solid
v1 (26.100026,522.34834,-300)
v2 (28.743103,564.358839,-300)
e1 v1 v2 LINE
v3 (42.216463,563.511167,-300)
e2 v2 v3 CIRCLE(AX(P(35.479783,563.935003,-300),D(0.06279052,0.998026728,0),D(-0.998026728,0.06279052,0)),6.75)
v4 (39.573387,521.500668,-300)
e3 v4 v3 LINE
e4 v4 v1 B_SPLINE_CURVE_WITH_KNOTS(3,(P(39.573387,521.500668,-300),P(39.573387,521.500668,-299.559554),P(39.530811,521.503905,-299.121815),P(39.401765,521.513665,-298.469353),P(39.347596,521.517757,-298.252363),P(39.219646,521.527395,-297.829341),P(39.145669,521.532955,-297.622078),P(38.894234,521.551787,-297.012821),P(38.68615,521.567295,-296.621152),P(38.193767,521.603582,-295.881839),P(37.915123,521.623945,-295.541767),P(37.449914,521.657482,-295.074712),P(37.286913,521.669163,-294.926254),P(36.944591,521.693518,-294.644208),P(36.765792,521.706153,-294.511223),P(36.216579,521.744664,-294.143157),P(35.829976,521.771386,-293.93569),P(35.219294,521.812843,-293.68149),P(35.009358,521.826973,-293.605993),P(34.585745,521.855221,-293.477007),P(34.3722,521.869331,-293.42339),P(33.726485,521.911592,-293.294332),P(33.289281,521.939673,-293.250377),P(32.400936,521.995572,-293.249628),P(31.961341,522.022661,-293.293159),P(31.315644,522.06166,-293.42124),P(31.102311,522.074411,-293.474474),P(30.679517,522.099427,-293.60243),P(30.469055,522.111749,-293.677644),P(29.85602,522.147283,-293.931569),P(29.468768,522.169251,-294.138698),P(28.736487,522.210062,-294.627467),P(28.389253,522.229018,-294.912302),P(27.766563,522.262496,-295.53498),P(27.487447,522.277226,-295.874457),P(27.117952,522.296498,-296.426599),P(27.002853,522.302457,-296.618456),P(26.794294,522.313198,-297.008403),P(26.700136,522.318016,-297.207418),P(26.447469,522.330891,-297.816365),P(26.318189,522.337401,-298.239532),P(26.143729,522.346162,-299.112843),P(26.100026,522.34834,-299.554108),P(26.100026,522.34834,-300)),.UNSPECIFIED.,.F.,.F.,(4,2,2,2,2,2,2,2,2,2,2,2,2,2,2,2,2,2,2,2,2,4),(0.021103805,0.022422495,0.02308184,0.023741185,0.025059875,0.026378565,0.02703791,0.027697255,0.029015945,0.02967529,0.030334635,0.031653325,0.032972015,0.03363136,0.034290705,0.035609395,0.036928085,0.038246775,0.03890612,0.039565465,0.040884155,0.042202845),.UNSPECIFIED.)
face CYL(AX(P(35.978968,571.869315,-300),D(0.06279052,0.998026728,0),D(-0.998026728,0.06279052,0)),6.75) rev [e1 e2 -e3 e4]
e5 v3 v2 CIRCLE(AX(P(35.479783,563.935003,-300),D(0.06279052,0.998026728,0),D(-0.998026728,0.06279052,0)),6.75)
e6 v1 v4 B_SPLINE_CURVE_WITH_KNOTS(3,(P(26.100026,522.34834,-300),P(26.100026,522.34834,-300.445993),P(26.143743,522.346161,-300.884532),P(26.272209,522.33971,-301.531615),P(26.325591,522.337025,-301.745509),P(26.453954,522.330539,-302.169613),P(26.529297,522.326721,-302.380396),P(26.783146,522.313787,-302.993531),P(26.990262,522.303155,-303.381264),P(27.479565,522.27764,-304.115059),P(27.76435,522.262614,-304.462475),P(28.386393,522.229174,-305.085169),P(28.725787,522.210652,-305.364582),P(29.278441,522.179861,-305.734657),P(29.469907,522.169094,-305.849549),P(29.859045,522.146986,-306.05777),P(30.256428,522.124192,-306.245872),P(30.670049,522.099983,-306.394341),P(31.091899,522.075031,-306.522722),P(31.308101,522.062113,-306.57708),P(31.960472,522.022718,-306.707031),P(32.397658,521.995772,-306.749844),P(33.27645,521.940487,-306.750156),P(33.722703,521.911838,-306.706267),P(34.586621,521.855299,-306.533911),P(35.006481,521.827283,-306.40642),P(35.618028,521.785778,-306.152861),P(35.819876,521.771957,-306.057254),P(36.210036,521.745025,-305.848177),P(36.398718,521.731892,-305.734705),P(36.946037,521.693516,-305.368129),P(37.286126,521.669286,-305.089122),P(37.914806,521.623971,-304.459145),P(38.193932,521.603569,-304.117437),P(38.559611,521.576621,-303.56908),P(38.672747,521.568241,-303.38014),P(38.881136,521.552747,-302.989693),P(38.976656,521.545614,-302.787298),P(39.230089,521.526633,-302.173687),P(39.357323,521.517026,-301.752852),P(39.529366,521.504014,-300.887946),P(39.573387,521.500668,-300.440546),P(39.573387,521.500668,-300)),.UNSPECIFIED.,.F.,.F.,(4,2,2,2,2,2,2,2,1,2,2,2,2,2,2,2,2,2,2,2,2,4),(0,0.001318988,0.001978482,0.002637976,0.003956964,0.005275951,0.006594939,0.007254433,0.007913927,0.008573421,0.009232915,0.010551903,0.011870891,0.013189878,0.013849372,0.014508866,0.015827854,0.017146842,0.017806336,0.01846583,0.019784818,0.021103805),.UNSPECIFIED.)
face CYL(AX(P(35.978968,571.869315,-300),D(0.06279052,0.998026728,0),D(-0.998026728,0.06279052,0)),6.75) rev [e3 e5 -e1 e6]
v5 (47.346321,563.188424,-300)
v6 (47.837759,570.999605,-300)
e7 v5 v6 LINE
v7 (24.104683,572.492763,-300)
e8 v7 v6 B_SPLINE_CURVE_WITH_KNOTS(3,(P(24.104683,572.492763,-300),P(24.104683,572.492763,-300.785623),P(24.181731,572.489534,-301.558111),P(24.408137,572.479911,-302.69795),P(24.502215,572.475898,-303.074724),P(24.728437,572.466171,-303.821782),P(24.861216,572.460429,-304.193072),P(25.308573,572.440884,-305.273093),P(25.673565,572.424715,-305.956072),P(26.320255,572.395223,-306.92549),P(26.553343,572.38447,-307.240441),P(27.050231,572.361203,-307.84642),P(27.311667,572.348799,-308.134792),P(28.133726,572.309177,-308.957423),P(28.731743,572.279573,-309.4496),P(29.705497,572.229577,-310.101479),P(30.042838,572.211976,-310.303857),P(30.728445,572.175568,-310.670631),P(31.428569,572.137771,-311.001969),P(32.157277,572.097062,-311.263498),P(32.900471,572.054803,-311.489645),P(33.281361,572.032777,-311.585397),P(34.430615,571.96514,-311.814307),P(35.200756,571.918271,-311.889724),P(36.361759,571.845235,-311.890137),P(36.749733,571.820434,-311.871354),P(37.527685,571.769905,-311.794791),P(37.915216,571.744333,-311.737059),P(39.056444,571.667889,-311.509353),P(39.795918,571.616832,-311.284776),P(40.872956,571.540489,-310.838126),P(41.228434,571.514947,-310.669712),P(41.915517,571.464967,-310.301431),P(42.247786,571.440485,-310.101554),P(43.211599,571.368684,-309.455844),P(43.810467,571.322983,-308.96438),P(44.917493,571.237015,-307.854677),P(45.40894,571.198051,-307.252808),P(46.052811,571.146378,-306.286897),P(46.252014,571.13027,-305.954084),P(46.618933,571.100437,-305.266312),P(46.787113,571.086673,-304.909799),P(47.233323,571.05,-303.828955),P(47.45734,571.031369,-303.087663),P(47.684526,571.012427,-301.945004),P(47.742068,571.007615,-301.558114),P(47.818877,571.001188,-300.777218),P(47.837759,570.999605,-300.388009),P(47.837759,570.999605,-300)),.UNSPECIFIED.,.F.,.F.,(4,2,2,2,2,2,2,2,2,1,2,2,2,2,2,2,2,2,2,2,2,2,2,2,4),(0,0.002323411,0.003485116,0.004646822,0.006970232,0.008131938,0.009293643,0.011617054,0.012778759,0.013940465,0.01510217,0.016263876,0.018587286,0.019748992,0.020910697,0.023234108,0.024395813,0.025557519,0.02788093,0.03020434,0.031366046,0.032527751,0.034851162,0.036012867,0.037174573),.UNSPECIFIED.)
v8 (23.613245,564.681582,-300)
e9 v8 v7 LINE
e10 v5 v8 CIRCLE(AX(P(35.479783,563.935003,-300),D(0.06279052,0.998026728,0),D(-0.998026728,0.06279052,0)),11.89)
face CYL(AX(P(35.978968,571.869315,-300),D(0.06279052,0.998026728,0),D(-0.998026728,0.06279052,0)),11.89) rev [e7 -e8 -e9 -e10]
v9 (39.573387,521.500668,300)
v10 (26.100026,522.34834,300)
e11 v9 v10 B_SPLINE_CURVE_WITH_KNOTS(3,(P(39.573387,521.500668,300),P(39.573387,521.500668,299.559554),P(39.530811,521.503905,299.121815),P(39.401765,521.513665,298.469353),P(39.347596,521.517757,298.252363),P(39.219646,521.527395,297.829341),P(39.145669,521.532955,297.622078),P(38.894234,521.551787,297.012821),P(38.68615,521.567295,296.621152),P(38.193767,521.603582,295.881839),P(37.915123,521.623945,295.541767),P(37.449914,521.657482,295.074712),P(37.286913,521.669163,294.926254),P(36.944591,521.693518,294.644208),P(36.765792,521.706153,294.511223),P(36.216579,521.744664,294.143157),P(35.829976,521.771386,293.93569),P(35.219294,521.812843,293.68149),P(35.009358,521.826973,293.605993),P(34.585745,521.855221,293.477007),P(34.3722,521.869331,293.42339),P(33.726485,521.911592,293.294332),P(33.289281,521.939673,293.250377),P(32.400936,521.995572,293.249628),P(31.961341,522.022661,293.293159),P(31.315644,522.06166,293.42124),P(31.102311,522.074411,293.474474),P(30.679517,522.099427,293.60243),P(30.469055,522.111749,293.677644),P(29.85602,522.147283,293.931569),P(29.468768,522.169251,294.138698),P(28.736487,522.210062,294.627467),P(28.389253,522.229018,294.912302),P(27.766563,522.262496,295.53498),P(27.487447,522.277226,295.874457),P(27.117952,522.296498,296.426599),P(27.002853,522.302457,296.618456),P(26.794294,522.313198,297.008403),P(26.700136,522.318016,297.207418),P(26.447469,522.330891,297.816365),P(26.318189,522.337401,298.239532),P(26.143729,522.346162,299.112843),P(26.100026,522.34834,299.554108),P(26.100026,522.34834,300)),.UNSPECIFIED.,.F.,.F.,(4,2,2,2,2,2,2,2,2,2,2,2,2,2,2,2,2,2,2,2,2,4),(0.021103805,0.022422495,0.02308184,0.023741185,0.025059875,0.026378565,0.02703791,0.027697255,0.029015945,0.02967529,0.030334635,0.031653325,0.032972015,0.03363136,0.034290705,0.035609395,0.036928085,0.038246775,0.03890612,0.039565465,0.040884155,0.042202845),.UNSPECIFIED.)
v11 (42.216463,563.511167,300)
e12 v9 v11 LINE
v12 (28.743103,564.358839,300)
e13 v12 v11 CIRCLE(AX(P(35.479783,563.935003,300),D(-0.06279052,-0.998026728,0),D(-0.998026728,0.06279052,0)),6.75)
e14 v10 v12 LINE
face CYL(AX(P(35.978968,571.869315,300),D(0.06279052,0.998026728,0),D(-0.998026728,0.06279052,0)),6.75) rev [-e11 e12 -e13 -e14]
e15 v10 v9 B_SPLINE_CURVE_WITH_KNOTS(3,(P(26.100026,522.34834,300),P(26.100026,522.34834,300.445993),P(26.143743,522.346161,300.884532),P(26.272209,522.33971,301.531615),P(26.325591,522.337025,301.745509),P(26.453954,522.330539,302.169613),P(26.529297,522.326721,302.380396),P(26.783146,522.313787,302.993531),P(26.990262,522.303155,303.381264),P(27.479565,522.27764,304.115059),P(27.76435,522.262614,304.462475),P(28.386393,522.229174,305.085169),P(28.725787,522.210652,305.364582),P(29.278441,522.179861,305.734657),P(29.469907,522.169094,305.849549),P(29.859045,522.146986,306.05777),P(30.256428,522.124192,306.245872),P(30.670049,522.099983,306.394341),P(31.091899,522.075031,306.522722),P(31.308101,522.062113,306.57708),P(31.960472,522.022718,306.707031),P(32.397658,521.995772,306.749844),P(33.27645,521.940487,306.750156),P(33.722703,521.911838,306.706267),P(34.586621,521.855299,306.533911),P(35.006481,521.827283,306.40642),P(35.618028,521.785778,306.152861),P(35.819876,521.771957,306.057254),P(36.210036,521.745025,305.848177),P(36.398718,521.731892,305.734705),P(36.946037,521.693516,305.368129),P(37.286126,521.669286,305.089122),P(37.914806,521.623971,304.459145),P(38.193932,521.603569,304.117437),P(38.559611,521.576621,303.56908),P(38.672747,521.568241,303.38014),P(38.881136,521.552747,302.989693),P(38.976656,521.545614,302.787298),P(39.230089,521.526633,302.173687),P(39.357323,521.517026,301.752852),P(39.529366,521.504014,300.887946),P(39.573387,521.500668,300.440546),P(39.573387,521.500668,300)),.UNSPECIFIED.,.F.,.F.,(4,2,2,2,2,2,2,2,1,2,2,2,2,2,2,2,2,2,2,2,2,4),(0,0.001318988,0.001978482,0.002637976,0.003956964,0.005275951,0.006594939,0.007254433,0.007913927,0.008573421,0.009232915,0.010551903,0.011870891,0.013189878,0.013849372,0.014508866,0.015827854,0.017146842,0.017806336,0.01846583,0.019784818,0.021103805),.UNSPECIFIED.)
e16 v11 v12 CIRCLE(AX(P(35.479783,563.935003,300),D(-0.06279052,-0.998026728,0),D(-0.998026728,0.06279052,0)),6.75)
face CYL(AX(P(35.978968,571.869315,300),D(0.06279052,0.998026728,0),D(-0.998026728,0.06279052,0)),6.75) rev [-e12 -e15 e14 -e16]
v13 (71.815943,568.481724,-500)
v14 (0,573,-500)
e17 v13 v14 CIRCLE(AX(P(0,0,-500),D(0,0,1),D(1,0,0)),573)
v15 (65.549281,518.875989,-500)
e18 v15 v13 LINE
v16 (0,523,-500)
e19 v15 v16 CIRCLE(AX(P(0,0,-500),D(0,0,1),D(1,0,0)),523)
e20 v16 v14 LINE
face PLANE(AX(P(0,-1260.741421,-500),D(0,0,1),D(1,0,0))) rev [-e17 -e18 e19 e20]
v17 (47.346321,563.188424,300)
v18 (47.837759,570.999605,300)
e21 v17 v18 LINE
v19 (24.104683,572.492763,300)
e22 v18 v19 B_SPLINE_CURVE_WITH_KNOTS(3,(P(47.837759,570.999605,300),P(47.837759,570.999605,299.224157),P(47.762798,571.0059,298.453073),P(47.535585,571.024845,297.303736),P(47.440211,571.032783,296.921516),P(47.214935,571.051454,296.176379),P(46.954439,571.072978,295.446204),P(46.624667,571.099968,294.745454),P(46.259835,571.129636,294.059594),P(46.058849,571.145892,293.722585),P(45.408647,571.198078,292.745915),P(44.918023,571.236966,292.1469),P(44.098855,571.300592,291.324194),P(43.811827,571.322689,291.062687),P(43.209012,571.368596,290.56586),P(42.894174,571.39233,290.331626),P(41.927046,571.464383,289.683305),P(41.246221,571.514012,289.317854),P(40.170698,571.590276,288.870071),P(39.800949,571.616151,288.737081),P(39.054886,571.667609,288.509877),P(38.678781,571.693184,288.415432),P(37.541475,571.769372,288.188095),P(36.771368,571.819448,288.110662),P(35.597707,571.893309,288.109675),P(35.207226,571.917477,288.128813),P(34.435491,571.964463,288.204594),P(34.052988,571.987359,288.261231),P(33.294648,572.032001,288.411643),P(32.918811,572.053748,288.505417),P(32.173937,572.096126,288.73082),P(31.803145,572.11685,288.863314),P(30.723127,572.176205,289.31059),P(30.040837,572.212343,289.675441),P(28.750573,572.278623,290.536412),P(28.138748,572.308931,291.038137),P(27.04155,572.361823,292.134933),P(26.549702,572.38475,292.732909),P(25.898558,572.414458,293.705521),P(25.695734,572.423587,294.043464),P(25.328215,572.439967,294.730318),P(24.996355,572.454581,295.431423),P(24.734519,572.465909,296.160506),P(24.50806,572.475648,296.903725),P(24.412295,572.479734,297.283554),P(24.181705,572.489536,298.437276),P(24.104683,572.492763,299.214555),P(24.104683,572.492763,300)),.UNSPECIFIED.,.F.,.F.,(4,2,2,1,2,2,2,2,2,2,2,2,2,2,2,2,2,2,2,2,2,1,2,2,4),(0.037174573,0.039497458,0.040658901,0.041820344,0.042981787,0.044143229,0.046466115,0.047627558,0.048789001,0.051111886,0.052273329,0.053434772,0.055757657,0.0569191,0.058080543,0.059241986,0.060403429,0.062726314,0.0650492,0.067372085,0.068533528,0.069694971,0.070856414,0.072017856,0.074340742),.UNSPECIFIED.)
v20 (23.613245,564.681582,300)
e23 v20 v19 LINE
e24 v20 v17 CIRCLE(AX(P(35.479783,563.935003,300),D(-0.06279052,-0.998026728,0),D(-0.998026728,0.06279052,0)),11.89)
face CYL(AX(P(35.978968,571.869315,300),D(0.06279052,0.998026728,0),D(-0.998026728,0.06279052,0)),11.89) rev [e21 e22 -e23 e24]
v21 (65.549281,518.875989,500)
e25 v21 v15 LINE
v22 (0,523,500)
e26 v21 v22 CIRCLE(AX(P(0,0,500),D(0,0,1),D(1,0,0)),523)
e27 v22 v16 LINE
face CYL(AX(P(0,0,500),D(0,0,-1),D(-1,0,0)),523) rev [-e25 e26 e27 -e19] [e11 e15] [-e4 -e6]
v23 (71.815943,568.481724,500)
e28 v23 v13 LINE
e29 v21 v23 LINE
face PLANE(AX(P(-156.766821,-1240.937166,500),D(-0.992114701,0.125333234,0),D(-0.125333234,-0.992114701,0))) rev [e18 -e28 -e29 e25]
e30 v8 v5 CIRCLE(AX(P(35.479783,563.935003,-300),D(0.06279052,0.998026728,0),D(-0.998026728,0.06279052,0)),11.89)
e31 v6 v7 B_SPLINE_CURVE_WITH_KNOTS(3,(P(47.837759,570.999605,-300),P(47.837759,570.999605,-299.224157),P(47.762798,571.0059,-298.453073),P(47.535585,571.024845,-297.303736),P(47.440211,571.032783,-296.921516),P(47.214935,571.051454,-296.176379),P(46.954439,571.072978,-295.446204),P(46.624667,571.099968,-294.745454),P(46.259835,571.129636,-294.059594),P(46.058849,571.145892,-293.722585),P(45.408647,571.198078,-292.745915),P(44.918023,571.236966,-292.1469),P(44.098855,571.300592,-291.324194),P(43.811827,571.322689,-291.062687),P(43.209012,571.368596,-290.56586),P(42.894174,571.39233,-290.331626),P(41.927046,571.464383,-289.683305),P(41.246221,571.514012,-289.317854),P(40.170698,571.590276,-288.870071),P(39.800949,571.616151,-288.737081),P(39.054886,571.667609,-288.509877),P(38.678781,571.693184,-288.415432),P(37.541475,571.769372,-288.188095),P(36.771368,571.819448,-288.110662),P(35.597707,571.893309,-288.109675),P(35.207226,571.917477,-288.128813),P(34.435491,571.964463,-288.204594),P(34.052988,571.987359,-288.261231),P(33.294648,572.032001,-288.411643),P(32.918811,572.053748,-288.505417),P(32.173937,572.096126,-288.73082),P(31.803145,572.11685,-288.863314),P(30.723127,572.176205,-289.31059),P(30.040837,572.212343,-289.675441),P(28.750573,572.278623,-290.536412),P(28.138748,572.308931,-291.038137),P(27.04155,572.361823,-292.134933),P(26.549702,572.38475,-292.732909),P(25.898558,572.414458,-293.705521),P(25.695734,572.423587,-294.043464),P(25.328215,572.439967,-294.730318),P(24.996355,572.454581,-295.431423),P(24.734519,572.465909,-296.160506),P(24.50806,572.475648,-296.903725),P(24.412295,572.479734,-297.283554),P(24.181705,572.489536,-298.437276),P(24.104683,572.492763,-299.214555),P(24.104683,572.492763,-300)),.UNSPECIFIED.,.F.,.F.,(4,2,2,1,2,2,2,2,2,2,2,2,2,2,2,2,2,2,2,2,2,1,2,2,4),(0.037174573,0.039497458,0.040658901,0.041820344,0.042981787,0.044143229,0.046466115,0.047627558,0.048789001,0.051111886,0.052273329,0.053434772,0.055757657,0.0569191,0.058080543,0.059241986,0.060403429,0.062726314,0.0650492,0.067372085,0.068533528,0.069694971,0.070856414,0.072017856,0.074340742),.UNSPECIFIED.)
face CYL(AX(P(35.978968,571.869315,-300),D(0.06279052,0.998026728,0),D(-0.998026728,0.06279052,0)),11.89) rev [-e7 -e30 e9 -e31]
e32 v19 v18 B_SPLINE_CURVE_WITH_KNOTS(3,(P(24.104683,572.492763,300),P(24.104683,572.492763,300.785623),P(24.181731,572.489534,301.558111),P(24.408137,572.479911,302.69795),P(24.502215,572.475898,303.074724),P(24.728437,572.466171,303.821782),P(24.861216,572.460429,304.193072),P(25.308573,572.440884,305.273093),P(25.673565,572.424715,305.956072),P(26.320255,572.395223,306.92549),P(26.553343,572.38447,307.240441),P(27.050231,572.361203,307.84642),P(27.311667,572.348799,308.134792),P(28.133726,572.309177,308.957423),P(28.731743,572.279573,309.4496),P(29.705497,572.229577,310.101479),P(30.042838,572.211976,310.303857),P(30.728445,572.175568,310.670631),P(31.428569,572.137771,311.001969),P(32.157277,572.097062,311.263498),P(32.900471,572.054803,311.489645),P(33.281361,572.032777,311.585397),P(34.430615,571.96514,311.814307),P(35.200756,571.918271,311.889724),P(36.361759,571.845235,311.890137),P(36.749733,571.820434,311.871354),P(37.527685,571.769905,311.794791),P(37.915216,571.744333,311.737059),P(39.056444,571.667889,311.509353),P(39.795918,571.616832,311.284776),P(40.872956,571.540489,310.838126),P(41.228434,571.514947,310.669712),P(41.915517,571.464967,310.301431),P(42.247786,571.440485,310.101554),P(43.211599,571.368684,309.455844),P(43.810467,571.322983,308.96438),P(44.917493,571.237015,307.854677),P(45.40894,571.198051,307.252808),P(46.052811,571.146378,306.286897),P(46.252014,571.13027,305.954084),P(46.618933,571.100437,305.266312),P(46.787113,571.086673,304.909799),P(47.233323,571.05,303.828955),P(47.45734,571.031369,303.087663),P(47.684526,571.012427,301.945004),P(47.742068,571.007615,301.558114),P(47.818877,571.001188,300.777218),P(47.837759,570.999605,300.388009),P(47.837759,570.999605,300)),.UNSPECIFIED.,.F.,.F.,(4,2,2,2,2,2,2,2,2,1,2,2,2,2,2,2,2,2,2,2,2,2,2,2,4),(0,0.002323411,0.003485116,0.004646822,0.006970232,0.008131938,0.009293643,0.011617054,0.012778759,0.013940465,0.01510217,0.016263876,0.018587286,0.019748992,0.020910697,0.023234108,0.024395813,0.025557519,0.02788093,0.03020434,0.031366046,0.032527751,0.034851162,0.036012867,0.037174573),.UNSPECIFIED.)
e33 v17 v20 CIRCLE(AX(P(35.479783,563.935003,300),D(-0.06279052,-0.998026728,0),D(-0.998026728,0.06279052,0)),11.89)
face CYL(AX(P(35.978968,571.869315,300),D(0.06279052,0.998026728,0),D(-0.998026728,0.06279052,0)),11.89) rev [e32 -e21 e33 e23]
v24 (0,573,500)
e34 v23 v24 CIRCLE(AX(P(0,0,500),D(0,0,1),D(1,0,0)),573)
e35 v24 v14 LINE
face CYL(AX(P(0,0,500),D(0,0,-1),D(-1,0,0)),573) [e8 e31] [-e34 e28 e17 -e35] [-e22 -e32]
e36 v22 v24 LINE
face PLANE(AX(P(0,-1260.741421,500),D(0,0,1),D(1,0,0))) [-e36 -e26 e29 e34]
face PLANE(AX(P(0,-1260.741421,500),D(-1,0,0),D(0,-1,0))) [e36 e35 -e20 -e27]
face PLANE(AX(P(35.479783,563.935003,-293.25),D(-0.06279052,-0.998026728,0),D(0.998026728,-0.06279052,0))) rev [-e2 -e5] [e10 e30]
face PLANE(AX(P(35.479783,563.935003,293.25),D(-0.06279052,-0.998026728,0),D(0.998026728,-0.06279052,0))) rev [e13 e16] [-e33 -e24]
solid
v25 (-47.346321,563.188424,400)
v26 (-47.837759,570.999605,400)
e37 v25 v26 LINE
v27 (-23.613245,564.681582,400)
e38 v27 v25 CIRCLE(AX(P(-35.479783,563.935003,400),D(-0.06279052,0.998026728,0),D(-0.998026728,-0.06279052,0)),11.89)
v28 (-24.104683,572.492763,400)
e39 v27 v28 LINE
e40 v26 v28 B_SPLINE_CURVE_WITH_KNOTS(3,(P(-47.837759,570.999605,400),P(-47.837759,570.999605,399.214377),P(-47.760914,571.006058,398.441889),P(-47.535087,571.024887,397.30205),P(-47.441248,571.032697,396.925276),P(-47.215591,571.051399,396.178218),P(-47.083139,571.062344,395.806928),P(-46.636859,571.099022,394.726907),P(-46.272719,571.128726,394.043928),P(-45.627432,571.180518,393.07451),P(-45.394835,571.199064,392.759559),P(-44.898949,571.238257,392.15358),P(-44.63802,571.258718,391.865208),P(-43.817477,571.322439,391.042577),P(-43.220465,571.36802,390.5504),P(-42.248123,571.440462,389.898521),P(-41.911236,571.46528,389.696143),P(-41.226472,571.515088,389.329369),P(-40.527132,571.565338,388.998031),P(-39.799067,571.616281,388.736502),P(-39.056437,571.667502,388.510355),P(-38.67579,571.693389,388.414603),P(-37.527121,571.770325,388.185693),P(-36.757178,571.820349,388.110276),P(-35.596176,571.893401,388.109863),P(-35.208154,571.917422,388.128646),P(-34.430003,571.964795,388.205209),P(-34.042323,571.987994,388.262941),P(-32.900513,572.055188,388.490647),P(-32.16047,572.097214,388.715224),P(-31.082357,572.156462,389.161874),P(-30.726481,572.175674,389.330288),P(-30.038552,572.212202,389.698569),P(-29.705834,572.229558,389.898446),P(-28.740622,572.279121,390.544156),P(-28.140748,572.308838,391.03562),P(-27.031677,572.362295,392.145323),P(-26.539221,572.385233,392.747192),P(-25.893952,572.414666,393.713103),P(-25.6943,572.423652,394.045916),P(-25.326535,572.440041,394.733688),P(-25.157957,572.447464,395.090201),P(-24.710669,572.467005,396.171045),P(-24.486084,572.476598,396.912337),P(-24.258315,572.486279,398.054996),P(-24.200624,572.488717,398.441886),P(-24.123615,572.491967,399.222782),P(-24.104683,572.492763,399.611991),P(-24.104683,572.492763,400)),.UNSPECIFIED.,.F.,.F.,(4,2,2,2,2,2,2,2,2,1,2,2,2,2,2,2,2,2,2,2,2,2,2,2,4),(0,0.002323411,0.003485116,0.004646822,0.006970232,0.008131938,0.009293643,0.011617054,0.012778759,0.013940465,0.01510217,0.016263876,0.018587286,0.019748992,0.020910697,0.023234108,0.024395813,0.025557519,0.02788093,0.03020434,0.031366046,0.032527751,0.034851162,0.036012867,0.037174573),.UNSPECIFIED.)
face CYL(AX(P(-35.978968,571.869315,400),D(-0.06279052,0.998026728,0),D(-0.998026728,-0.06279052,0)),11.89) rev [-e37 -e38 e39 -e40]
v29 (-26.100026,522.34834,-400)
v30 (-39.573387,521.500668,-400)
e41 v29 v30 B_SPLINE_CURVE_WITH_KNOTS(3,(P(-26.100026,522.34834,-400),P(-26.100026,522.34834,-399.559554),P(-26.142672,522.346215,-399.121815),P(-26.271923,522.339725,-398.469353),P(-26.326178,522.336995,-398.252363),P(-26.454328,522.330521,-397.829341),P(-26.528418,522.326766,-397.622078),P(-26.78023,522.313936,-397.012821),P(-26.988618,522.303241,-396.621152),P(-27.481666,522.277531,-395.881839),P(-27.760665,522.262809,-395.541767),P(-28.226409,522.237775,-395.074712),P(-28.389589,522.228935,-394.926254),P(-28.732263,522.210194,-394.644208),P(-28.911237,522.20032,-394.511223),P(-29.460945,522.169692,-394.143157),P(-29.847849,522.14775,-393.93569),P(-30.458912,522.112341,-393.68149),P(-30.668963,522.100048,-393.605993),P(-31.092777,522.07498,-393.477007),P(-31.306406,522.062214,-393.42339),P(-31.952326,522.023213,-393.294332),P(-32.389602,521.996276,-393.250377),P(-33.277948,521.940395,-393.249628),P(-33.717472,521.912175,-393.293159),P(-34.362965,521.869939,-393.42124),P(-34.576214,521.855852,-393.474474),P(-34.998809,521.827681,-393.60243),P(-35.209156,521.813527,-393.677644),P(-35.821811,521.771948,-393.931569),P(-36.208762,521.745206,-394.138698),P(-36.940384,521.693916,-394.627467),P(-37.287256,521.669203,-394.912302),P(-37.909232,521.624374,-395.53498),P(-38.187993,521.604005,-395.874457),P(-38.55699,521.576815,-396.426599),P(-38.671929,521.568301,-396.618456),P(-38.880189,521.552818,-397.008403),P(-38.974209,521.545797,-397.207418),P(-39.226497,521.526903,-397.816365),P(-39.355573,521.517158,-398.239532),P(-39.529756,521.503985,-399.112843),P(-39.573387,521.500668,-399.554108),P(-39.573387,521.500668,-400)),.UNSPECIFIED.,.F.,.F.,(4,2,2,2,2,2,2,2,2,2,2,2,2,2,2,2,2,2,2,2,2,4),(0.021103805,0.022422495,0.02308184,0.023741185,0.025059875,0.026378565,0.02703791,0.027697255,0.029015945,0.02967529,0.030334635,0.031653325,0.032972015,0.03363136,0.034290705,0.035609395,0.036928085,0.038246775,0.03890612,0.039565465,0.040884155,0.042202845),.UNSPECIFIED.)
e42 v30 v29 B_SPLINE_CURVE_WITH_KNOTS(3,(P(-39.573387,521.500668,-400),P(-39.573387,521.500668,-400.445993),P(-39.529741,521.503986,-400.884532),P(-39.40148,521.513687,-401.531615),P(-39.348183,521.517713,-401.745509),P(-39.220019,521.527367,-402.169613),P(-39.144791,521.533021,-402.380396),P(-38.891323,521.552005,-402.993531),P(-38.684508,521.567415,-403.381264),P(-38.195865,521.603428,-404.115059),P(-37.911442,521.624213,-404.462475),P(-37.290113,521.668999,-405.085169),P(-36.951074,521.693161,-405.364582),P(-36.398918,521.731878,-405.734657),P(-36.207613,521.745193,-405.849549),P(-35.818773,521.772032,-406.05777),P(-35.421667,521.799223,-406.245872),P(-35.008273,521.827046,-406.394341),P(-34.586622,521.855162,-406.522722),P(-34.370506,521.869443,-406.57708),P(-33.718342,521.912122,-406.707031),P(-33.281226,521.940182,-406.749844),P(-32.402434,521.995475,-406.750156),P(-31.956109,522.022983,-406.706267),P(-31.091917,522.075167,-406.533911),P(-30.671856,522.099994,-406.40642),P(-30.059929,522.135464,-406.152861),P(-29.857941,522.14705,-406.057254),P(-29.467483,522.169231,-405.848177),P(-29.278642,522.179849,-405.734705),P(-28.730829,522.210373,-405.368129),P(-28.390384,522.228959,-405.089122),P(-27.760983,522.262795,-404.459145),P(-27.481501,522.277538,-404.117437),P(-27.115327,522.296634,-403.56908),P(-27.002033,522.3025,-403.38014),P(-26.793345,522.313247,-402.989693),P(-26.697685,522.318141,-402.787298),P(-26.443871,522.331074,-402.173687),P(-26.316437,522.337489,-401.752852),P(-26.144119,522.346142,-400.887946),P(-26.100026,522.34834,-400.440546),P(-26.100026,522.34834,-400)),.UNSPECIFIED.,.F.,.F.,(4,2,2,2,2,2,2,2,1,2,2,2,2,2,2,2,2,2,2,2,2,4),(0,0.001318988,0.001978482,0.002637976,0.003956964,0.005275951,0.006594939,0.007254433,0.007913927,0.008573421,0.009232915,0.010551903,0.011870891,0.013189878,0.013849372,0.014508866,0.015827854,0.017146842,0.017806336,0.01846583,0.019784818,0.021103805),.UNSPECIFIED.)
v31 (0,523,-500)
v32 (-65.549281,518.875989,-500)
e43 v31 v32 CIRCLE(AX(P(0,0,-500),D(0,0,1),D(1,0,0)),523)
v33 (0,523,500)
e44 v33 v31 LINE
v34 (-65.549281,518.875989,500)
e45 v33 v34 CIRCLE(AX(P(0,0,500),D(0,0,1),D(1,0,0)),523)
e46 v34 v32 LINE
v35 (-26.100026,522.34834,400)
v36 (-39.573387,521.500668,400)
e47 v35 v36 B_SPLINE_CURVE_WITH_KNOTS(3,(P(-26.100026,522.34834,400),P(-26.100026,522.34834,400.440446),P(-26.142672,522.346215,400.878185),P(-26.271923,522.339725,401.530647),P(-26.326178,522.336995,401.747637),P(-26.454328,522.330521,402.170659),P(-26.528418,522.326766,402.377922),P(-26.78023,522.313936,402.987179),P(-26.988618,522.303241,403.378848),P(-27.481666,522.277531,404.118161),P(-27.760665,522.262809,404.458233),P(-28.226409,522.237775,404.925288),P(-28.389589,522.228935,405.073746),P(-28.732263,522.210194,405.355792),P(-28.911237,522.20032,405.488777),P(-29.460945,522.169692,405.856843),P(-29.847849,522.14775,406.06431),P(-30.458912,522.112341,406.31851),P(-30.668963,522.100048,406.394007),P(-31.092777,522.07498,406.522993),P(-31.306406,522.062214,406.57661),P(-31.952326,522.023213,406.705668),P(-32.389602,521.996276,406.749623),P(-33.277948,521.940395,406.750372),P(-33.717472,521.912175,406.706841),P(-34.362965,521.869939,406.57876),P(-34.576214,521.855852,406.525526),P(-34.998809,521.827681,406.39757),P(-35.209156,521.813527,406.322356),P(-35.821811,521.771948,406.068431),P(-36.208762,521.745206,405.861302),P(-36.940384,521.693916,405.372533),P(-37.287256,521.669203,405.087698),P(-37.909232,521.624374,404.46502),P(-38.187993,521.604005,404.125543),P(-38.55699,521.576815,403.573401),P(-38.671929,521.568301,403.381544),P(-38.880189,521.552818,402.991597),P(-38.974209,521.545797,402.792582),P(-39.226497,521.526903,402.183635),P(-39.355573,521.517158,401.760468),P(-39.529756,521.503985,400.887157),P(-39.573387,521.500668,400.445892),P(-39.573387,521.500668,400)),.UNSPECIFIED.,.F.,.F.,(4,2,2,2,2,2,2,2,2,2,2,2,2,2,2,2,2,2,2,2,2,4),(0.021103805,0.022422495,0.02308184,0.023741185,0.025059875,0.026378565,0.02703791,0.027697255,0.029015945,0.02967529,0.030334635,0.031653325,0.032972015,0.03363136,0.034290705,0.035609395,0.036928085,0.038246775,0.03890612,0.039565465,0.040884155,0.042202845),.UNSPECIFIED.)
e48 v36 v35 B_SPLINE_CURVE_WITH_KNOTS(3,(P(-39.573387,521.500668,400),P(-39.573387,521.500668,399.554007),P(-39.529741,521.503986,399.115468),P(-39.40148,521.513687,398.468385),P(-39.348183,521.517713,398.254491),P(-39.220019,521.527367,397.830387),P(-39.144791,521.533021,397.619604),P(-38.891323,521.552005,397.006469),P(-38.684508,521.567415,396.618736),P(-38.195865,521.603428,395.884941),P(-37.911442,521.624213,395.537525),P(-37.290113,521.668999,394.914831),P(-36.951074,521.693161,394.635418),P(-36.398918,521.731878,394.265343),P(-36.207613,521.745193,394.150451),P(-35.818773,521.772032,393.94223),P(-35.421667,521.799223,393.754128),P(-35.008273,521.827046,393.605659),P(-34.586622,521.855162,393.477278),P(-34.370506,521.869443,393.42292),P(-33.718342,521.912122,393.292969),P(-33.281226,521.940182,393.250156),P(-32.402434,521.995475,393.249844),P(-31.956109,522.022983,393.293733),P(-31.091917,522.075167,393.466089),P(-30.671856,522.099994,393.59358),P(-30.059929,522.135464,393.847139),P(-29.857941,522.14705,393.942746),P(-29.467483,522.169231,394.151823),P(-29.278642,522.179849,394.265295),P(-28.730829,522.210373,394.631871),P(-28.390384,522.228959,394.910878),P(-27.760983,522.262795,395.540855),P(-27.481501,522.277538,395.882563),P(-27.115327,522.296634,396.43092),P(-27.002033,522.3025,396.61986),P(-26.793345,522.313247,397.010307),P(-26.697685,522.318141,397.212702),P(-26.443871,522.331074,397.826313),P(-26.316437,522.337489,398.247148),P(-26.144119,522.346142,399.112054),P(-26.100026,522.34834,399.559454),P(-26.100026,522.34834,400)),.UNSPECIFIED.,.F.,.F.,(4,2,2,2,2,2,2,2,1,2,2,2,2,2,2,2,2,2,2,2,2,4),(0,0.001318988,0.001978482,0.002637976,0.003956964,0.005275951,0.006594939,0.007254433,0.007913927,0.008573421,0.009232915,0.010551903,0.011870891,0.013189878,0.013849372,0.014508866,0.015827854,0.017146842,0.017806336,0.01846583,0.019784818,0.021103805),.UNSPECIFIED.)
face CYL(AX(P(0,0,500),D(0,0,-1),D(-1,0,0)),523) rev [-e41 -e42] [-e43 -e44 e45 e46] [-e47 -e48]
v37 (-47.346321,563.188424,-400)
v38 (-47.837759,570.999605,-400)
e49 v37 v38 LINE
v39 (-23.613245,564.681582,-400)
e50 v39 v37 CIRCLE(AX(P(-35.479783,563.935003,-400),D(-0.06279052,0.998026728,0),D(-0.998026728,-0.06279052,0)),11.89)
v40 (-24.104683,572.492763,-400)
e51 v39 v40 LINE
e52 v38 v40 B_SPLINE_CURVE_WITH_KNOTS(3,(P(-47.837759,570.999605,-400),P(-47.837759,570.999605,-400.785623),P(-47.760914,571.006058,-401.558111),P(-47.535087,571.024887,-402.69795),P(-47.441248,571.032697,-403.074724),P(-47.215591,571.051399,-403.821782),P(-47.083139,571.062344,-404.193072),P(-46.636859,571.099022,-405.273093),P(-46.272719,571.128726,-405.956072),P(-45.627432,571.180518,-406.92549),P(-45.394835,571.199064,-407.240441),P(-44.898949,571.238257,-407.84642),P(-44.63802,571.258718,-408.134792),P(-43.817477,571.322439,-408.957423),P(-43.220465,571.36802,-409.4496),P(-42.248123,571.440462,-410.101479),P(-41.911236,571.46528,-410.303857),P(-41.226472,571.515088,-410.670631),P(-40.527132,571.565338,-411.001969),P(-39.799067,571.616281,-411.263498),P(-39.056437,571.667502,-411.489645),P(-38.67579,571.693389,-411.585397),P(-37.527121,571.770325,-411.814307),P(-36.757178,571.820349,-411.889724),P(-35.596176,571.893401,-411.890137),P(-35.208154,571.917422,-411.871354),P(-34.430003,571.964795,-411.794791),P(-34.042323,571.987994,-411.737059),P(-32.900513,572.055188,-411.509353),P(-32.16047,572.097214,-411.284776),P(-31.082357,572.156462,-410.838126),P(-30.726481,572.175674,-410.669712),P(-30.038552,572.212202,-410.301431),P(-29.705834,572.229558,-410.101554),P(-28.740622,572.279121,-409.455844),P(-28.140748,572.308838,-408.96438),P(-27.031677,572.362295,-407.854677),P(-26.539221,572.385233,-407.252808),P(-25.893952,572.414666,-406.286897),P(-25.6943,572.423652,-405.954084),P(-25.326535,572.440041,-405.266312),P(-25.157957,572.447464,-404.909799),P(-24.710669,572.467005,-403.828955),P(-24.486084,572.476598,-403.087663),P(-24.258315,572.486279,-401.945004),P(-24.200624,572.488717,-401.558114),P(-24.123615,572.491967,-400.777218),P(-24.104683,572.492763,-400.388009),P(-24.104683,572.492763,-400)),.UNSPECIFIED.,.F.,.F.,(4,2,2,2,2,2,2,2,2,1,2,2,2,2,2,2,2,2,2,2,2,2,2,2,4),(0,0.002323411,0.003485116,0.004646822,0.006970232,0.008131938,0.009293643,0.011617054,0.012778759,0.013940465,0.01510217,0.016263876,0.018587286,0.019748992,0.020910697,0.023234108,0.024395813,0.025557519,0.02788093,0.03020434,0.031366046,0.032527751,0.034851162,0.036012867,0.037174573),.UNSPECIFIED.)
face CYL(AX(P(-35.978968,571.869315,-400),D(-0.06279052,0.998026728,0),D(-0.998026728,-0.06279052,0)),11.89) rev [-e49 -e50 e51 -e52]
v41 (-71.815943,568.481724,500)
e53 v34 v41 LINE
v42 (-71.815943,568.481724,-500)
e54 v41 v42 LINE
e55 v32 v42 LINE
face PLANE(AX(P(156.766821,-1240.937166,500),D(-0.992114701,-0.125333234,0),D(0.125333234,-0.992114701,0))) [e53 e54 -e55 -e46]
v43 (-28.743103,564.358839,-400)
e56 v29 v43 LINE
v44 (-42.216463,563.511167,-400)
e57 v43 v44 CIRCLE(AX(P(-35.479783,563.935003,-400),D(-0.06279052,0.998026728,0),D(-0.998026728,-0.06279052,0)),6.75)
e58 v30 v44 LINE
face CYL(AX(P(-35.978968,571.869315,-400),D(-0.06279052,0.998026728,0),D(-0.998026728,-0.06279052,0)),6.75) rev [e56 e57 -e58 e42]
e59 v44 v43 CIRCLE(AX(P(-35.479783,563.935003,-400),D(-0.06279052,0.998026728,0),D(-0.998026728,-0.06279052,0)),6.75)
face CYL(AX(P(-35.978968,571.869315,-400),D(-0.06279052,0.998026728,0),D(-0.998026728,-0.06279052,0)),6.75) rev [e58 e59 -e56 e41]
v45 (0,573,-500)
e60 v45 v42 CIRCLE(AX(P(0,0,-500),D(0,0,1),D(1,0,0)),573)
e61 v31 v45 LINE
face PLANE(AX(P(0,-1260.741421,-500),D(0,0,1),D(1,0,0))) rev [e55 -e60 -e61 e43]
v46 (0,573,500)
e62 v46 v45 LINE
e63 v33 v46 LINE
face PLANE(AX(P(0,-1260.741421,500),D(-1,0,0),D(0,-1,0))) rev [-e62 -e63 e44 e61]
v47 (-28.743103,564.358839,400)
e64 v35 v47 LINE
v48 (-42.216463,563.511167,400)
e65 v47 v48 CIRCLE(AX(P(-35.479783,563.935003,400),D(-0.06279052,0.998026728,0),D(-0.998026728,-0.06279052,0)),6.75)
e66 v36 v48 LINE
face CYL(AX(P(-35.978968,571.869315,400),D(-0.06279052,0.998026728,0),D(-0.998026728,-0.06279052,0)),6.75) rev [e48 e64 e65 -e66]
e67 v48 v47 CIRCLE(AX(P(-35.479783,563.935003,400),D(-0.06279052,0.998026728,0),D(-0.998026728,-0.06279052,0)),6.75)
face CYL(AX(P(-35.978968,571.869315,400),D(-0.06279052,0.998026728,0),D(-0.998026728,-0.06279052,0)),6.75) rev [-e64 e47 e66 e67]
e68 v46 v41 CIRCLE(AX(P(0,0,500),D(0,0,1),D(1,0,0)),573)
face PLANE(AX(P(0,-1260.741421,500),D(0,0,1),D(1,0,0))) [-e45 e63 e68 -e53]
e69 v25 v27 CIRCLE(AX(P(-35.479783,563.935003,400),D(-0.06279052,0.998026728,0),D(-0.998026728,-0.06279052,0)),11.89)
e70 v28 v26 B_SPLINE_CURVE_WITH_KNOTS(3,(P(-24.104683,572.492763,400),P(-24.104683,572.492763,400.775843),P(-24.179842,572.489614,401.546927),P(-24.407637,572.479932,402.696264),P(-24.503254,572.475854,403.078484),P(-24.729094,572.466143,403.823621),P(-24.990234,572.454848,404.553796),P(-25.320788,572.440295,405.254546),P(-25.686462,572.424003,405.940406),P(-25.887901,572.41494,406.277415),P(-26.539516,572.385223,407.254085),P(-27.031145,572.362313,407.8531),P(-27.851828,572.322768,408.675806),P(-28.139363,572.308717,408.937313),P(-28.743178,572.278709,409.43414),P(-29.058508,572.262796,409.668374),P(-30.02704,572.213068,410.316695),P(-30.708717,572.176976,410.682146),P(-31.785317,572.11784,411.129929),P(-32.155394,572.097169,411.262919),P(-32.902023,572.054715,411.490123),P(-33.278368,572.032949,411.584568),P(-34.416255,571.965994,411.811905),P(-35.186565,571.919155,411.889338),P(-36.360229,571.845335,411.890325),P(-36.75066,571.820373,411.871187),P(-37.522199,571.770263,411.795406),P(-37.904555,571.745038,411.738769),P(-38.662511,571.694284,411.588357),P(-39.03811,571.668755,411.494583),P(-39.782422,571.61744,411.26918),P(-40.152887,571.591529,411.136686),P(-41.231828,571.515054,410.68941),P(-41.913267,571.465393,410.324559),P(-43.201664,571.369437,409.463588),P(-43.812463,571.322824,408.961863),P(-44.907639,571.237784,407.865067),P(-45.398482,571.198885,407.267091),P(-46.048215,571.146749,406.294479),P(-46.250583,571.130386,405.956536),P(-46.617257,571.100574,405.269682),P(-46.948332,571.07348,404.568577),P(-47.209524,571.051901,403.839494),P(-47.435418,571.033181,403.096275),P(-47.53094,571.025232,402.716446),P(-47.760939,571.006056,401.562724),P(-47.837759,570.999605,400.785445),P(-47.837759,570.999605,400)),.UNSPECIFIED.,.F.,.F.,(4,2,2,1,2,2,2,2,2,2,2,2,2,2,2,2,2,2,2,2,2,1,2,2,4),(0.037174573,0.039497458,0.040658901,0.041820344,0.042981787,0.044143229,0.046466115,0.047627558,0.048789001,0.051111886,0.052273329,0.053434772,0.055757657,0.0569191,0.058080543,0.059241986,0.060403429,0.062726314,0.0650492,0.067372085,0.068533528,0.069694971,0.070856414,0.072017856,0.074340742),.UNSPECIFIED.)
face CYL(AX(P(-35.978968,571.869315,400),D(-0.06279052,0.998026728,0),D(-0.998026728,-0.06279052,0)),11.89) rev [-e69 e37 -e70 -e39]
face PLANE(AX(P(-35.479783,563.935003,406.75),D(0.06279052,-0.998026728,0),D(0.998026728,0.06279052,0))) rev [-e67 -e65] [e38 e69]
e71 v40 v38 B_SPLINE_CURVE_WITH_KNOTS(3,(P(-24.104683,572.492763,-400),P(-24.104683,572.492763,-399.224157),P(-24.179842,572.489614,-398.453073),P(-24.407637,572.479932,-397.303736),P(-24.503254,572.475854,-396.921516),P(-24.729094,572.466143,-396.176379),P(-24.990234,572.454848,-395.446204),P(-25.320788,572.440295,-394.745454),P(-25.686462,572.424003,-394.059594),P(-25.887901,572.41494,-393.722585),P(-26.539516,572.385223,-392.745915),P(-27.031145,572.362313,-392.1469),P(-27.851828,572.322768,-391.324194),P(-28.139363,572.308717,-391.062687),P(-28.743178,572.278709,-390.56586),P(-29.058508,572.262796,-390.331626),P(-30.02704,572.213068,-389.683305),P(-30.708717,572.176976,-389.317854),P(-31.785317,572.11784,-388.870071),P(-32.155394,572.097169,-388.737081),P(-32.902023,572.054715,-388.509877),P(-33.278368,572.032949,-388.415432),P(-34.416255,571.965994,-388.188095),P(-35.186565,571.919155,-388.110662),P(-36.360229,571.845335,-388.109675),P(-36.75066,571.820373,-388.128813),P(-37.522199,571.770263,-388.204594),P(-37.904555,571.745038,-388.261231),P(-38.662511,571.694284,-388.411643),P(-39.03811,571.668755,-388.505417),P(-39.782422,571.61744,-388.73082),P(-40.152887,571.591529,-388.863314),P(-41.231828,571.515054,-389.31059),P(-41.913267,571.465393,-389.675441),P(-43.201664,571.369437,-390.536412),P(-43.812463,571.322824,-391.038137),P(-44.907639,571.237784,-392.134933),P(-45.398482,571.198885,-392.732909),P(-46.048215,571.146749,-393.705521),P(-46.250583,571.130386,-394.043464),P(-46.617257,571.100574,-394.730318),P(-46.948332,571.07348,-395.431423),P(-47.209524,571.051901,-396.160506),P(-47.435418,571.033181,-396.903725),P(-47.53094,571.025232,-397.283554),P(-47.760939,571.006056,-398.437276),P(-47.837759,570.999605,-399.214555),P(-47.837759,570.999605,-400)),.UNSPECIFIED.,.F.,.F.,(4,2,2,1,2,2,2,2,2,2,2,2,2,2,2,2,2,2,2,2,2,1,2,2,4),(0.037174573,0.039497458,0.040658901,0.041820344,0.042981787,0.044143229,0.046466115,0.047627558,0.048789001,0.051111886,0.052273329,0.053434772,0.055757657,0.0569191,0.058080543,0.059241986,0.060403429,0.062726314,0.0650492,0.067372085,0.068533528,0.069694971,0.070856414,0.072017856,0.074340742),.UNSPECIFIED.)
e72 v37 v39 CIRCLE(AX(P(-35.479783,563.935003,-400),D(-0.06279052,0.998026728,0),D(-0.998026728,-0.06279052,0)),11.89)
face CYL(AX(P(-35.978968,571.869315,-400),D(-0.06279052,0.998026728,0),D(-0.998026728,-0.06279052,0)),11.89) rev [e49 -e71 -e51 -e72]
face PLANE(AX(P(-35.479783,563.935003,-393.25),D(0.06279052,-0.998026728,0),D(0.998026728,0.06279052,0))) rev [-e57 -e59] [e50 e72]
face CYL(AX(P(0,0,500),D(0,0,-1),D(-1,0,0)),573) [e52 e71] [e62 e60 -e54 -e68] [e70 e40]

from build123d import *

# Parameters (mm, degrees)
BOSS_EXTRUDE1_DEPTH = 500
BOSS_EXTRUDE2_DEPTH = 500


with BuildPart() as part:
    # Sketch 1_3 → Boss-Extrude1 (new, symmetric)
    with BuildSketch(Plane.XY):
        with BuildLine():
            Line((-71.815942832, 568.481723853), (-65.549281154, 518.875988787))
            ThreePointArc((-65.549281154, 518.875988787), (-32.839441714, 521.967978968), (0, 523))
            Line((0, 523), (0, 573))
            ThreePointArc((0, 573), (-35.97896769, 571.869315389), (-71.815942832, 568.481723853))
        make_face()
    extrude(amount=BOSS_EXTRUDE1_DEPTH, both=True)

    # Sketch7 → CBORE for M12 Hex Head Bolt1 (revolve, cut)
    with BuildSketch(Plane(origin=(-35.97896769, 571.869315389, -400), x_dir=(-0.9980267284282717, -0.06279051952931308, 0), z_dir=(0, 0, 1))):
        Polygon((0, 0), (0, 55.14789445), (6.75, 55.14789445), (6.75, 7.95), (11.89, 7.95), (11.89, 0), align=None)
    cbore_for_m12_hex_head_bolt1 = revolve(axis=Axis((-36.377687489, 578.206785115, -400), (0.0627905195293131, -0.9980267284282717, 0)), mode=Mode.SUBTRACT)

    # Mirror2: CBORE for M12 Hex Head Bolt1 across plane
    add(cbore_for_m12_hex_head_bolt1.mirror(Plane.XY), mode=Mode.SUBTRACT)


with BuildPart() as body_2:
    # Sketch 1_3 2 → Boss-Extrude2 (new, symmetric)
    with BuildSketch(Plane.XY):
        with BuildLine():
            Line((0, 573), (0, 523))
            ThreePointArc((0, 523), (32.839441714, 521.967978968), (65.549281154, 518.875988787))
            Line((65.549281154, 518.875988787), (71.815942832, 568.481723853))
            ThreePointArc((71.815942832, 568.481723853), (35.97896769, 571.869315389), (0, 573))
        make_face()
    extrude(amount=BOSS_EXTRUDE2_DEPTH, both=True)

    # Sketch9 → CBORE for M12 Hex Head Bolt2 (revolve, cut)
    with BuildSketch(Plane(origin=(35.97896769, 571.869315389, -300), x_dir=(-0.9980267284282716, 0.06279051952931385, 0), z_dir=(0, 0, 1))):
        Polygon((0, 0), (0, 59.657254811), (6.75, 59.657254811), (6.75, 7.95), (11.89, 7.95), (11.89, 0), align=None)
    cbore_for_m12_hex_head_bolt2 = revolve(axis=Axis((36.377687489, 578.206785115, -300), (-0.0627905195293138, -0.9980267284282716, 0)), mode=Mode.SUBTRACT)

    # Mirror1: CBORE for M12 Hex Head Bolt2 across plane
    add(cbore_for_m12_hex_head_bolt2.mirror(Plane.XY), mode=Mode.SUBTRACT)


solid = Compound([part.part, body_2.part])
